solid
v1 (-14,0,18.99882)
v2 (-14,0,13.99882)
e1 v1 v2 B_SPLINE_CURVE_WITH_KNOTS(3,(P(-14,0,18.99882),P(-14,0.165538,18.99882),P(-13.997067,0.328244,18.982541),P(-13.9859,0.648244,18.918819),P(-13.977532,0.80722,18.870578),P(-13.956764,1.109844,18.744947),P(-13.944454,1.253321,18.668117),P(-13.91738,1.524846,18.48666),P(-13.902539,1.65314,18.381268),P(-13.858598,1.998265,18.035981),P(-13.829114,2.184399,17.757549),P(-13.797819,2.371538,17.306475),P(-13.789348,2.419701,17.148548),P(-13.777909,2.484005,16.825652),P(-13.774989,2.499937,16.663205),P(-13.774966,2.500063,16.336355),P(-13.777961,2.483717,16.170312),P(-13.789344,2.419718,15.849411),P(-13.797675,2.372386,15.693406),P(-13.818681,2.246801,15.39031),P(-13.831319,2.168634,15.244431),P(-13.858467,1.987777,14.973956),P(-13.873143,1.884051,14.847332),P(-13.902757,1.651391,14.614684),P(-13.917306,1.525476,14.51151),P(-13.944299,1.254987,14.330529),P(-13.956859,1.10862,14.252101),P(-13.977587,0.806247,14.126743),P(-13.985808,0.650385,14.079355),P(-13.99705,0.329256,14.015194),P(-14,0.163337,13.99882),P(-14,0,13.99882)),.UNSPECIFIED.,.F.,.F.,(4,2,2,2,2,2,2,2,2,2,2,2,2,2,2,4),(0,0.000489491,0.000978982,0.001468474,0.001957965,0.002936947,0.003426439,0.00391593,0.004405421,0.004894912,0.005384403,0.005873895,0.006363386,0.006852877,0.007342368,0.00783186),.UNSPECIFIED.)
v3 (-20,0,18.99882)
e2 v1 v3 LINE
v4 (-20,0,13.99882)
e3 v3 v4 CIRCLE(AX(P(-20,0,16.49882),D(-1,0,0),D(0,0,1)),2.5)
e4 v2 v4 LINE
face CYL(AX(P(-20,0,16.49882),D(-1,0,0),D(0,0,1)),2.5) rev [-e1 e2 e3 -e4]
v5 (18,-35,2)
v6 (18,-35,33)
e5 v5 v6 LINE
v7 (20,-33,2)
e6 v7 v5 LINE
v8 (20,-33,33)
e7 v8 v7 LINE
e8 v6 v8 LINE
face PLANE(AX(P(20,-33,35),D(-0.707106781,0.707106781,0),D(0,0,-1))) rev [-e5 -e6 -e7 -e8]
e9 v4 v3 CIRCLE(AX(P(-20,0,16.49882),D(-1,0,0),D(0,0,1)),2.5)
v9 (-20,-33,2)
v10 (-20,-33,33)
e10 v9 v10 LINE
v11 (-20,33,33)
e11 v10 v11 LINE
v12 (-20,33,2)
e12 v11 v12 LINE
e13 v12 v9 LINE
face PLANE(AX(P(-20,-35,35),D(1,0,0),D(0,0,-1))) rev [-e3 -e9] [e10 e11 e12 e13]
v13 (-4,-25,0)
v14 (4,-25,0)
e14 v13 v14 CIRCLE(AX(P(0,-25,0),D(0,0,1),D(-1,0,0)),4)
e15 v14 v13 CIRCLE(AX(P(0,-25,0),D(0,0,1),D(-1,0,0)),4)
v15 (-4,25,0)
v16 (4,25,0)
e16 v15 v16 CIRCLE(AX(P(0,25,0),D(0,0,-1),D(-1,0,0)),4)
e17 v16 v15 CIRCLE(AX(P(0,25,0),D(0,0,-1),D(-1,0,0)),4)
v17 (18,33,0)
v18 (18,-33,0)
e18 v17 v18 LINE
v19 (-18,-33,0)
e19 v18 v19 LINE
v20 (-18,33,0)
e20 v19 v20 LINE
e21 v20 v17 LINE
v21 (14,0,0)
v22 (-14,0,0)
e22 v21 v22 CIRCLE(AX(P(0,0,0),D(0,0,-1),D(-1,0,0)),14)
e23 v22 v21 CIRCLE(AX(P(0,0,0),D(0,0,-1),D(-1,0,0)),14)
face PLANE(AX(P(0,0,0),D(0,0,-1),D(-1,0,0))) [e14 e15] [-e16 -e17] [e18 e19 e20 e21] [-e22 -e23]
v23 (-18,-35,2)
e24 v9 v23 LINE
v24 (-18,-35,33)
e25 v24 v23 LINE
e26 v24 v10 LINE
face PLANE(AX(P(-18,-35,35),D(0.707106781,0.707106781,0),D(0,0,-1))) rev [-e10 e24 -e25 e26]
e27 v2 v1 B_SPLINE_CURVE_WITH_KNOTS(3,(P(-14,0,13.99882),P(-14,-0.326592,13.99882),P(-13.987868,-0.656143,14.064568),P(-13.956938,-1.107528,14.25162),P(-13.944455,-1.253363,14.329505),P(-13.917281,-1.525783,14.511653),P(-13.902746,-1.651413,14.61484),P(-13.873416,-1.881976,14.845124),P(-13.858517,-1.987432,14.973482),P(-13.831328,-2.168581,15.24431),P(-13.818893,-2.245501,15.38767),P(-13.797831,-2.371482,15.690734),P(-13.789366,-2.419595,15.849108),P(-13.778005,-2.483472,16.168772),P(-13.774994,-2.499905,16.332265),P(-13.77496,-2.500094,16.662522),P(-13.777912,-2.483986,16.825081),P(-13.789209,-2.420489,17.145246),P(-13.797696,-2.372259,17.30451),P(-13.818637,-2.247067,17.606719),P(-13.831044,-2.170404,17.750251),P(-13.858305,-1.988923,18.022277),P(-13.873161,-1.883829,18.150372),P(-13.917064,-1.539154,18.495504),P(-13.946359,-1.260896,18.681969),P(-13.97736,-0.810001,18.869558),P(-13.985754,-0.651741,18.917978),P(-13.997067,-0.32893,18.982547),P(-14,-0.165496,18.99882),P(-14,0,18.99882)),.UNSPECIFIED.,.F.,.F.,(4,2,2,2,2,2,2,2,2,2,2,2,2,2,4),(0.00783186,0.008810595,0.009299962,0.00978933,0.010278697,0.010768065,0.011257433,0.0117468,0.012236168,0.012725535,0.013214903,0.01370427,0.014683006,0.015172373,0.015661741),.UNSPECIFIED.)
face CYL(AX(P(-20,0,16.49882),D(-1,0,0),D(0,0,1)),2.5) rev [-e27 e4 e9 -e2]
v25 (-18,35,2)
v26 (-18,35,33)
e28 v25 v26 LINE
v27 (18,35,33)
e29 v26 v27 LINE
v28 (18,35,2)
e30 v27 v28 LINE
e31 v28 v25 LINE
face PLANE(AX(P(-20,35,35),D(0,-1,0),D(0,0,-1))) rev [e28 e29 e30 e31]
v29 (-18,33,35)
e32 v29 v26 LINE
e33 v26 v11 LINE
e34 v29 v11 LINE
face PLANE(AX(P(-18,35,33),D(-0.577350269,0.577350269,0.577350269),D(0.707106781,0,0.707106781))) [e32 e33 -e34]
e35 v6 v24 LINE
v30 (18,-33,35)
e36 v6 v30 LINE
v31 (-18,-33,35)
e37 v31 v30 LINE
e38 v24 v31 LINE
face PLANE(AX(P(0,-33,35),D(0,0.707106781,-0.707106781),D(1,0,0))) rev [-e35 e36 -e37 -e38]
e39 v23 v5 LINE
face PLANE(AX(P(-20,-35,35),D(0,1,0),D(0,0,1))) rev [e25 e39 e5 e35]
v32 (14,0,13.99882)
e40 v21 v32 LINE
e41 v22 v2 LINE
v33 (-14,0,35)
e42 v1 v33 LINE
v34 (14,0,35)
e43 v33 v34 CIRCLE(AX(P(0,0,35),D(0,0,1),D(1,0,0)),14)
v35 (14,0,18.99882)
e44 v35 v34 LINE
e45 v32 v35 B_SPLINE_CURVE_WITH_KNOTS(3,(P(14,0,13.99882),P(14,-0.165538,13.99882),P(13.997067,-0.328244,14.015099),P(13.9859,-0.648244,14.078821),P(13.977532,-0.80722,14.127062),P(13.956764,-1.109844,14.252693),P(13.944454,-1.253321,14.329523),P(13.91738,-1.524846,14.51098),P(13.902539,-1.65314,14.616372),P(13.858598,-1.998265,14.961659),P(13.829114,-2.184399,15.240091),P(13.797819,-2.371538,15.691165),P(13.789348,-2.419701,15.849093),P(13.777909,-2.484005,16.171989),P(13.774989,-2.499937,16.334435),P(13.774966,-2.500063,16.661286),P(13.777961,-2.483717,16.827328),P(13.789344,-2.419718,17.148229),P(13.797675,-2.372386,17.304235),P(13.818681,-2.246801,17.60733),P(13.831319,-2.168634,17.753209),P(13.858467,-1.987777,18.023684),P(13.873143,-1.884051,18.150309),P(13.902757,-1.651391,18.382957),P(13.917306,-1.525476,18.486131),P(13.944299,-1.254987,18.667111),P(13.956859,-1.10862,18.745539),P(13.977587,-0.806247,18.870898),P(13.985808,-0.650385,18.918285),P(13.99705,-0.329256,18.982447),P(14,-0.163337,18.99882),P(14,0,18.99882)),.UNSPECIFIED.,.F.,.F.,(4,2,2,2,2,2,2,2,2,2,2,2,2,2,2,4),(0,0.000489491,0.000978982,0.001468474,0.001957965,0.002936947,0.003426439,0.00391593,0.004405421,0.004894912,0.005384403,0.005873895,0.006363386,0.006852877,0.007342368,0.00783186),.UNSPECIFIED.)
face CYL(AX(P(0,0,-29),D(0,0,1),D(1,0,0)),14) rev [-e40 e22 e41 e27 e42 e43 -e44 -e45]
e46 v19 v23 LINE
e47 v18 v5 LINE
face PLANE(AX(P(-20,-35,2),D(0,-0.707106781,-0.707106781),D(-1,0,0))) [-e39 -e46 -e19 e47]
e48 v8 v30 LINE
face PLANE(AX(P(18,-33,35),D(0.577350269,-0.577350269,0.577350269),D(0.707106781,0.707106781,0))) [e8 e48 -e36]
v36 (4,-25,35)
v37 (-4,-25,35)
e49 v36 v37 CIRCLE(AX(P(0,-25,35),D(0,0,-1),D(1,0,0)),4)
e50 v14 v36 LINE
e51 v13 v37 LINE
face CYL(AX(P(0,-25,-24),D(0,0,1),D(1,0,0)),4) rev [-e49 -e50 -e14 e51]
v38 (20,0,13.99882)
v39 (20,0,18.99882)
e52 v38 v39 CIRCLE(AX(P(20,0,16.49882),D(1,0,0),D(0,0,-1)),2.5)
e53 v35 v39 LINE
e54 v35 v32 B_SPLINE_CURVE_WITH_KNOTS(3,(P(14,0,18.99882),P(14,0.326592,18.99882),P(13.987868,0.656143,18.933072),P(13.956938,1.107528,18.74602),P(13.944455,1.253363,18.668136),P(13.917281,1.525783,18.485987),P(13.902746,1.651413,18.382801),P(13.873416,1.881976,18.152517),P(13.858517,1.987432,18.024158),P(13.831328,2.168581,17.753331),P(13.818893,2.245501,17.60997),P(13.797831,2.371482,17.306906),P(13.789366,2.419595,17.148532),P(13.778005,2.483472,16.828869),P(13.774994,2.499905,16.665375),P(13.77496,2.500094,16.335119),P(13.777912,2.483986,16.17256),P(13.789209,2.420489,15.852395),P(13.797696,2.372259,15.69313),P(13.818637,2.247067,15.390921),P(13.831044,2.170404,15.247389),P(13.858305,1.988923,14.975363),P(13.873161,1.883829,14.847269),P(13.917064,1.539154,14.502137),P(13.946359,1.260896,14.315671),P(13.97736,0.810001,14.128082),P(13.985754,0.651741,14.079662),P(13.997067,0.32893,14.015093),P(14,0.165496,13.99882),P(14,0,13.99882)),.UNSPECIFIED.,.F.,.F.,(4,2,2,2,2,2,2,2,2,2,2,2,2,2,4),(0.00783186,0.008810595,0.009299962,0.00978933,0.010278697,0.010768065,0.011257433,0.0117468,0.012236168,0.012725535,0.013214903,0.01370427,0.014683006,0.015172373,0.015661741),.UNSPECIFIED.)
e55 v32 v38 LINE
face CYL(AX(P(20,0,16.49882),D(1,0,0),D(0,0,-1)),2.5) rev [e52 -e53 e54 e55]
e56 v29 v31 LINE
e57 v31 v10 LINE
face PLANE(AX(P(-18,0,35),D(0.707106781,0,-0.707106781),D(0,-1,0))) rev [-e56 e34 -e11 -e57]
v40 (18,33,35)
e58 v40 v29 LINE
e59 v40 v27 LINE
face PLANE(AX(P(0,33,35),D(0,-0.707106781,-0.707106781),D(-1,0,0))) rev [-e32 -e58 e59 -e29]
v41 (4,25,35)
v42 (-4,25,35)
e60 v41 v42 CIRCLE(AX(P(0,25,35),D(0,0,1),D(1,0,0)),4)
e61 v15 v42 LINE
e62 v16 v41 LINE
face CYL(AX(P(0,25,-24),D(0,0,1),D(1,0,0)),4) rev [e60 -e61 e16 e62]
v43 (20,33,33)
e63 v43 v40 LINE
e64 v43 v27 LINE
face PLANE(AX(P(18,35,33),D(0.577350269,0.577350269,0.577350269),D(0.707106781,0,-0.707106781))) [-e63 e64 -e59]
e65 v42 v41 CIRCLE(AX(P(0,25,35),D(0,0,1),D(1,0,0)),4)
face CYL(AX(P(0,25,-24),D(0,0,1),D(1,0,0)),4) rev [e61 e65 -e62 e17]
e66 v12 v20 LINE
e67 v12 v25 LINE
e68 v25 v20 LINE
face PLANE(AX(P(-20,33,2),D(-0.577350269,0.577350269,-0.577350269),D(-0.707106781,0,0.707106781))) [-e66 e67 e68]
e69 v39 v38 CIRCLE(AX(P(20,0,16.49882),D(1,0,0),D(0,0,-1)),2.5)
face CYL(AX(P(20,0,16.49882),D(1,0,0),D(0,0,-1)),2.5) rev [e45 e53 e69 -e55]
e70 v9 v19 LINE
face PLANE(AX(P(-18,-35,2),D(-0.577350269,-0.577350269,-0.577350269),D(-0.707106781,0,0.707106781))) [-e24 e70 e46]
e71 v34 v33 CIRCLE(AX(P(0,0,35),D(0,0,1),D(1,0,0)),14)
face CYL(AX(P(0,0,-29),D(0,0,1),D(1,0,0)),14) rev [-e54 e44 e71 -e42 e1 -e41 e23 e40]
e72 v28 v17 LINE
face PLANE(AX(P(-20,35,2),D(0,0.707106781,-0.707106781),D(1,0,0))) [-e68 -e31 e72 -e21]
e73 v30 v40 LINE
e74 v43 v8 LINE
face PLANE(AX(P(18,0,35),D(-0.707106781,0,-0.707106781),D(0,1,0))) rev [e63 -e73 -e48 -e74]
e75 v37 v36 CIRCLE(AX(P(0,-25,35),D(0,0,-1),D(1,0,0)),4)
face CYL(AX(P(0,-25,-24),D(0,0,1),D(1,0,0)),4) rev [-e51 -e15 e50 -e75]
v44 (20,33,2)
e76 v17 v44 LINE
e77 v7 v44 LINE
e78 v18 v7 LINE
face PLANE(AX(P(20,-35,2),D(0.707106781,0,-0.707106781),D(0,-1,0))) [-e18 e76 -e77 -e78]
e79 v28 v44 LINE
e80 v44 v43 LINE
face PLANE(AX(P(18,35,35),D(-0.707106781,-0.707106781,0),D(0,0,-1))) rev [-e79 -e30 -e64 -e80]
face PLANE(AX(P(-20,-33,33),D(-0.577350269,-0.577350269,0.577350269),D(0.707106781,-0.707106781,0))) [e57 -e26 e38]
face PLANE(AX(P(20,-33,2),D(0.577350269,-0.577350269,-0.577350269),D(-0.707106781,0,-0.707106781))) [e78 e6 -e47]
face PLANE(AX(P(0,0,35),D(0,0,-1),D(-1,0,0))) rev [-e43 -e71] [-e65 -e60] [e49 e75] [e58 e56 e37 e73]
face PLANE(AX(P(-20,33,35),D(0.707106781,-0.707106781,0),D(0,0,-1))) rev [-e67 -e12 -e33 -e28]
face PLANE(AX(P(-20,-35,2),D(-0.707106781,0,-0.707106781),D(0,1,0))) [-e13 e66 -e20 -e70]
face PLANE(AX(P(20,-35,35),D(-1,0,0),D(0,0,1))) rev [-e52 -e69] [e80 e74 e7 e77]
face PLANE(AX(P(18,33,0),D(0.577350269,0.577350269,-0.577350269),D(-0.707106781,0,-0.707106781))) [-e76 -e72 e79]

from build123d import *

# Parameters (mm, degrees)
SKETCH_1_W              = 40
SKETCH_1_H              = 70
EXTRUDE_1_DEPTH         = 35
SKETCH_2_R              = 14
CUT_EXTRUDE_1_DEPTH     = 64
SKETCH_4_R              = 4
CUT_EXTRUDE_3_DEPTH     = 59
HOLE_WIZARD_M6_1_REACH  = 58.279
HOLE_WIZARD_M6_1_BORE_R = 2.5
CHAMFER_1_SIZE          = 2


with BuildPart() as part:
    # 草图1 → 凸台-拉伸1 (new body)
    with BuildSketch(Plane.XY):
        Rectangle(SKETCH_1_W, SKETCH_1_H)
    extrude(amount=EXTRUDE_1_DEPTH)

    # 草图2 → 切除-拉伸1 (cut)
    with BuildSketch(Plane.XY.offset(35)):
        Circle(SKETCH_2_R)
    extrude(amount=-CUT_EXTRUDE_1_DEPTH, mode=Mode.SUBTRACT)

    # 草图4 → 切除-拉伸3 (cut)
    with BuildSketch(Plane.XY.offset(35)):
        with Locations((0, 25)):
            Circle(SKETCH_4_R)
    cut_extrude_3 = extrude(amount=-CUT_EXTRUDE_3_DEPTH, mode=Mode.SUBTRACT)

    # M6 螺纹孔1 bore (on position points) → M6 螺纹孔1 (cut, up to next)
    with BuildSketch(Plane(origin=(-20, 0, 16.498820141), x_dir=(0, 0, -1), z_dir=(-1, 0, 0)), mode=Mode.PRIVATE) as hole_wizard_m6_1_sk1:
        Circle(HOLE_WIZARD_M6_1_BORE_R)
    hole_wizard_m6_1_tool1 = extrude(hole_wizard_m6_1_sk1.sketch, amount=-HOLE_WIZARD_M6_1_REACH, mode=Mode.PRIVATE) & part.part
    hole_wizard_m6_1 = hole_wizard_m6_1_tool1.solids().sort_by_distance((-20, 0, 16.49882))[0]
    add(hole_wizard_m6_1, mode=Mode.SUBTRACT)

    # 镜向2: 切除-拉伸3 across plane
    add(cut_extrude_3.mirror(Plane.ZX), mode=Mode.SUBTRACT)

    # 镜向3: M6 螺纹孔1 across plane
    add(hole_wizard_m6_1.mirror(Plane(origin=(0, 0, 0), x_dir=(0, 0, 1), z_dir=(1, 0, 0))), mode=Mode.SUBTRACT)

    # 倒角1
    chamfer_1_edges = [part.edges().sort_by_distance(p)[0] for p in [
        (-20, 0, 35),
        (0, -35, 35),
        (20, 0, 35),
        (0, -35, 0),
        (-20, 0, 0),
        (0, 35, 0),
        (20, 0, 0),
        (20, -35, 17.5),
        (-20, -35, 17.5),
        (-20, 35, 17.5),
        (20, 35, 17.5),
        (0, 35, 35),
    ]]
    chamfer(chamfer_1_edges, length=CHAMFER_1_SIZE)


solid = part.part
